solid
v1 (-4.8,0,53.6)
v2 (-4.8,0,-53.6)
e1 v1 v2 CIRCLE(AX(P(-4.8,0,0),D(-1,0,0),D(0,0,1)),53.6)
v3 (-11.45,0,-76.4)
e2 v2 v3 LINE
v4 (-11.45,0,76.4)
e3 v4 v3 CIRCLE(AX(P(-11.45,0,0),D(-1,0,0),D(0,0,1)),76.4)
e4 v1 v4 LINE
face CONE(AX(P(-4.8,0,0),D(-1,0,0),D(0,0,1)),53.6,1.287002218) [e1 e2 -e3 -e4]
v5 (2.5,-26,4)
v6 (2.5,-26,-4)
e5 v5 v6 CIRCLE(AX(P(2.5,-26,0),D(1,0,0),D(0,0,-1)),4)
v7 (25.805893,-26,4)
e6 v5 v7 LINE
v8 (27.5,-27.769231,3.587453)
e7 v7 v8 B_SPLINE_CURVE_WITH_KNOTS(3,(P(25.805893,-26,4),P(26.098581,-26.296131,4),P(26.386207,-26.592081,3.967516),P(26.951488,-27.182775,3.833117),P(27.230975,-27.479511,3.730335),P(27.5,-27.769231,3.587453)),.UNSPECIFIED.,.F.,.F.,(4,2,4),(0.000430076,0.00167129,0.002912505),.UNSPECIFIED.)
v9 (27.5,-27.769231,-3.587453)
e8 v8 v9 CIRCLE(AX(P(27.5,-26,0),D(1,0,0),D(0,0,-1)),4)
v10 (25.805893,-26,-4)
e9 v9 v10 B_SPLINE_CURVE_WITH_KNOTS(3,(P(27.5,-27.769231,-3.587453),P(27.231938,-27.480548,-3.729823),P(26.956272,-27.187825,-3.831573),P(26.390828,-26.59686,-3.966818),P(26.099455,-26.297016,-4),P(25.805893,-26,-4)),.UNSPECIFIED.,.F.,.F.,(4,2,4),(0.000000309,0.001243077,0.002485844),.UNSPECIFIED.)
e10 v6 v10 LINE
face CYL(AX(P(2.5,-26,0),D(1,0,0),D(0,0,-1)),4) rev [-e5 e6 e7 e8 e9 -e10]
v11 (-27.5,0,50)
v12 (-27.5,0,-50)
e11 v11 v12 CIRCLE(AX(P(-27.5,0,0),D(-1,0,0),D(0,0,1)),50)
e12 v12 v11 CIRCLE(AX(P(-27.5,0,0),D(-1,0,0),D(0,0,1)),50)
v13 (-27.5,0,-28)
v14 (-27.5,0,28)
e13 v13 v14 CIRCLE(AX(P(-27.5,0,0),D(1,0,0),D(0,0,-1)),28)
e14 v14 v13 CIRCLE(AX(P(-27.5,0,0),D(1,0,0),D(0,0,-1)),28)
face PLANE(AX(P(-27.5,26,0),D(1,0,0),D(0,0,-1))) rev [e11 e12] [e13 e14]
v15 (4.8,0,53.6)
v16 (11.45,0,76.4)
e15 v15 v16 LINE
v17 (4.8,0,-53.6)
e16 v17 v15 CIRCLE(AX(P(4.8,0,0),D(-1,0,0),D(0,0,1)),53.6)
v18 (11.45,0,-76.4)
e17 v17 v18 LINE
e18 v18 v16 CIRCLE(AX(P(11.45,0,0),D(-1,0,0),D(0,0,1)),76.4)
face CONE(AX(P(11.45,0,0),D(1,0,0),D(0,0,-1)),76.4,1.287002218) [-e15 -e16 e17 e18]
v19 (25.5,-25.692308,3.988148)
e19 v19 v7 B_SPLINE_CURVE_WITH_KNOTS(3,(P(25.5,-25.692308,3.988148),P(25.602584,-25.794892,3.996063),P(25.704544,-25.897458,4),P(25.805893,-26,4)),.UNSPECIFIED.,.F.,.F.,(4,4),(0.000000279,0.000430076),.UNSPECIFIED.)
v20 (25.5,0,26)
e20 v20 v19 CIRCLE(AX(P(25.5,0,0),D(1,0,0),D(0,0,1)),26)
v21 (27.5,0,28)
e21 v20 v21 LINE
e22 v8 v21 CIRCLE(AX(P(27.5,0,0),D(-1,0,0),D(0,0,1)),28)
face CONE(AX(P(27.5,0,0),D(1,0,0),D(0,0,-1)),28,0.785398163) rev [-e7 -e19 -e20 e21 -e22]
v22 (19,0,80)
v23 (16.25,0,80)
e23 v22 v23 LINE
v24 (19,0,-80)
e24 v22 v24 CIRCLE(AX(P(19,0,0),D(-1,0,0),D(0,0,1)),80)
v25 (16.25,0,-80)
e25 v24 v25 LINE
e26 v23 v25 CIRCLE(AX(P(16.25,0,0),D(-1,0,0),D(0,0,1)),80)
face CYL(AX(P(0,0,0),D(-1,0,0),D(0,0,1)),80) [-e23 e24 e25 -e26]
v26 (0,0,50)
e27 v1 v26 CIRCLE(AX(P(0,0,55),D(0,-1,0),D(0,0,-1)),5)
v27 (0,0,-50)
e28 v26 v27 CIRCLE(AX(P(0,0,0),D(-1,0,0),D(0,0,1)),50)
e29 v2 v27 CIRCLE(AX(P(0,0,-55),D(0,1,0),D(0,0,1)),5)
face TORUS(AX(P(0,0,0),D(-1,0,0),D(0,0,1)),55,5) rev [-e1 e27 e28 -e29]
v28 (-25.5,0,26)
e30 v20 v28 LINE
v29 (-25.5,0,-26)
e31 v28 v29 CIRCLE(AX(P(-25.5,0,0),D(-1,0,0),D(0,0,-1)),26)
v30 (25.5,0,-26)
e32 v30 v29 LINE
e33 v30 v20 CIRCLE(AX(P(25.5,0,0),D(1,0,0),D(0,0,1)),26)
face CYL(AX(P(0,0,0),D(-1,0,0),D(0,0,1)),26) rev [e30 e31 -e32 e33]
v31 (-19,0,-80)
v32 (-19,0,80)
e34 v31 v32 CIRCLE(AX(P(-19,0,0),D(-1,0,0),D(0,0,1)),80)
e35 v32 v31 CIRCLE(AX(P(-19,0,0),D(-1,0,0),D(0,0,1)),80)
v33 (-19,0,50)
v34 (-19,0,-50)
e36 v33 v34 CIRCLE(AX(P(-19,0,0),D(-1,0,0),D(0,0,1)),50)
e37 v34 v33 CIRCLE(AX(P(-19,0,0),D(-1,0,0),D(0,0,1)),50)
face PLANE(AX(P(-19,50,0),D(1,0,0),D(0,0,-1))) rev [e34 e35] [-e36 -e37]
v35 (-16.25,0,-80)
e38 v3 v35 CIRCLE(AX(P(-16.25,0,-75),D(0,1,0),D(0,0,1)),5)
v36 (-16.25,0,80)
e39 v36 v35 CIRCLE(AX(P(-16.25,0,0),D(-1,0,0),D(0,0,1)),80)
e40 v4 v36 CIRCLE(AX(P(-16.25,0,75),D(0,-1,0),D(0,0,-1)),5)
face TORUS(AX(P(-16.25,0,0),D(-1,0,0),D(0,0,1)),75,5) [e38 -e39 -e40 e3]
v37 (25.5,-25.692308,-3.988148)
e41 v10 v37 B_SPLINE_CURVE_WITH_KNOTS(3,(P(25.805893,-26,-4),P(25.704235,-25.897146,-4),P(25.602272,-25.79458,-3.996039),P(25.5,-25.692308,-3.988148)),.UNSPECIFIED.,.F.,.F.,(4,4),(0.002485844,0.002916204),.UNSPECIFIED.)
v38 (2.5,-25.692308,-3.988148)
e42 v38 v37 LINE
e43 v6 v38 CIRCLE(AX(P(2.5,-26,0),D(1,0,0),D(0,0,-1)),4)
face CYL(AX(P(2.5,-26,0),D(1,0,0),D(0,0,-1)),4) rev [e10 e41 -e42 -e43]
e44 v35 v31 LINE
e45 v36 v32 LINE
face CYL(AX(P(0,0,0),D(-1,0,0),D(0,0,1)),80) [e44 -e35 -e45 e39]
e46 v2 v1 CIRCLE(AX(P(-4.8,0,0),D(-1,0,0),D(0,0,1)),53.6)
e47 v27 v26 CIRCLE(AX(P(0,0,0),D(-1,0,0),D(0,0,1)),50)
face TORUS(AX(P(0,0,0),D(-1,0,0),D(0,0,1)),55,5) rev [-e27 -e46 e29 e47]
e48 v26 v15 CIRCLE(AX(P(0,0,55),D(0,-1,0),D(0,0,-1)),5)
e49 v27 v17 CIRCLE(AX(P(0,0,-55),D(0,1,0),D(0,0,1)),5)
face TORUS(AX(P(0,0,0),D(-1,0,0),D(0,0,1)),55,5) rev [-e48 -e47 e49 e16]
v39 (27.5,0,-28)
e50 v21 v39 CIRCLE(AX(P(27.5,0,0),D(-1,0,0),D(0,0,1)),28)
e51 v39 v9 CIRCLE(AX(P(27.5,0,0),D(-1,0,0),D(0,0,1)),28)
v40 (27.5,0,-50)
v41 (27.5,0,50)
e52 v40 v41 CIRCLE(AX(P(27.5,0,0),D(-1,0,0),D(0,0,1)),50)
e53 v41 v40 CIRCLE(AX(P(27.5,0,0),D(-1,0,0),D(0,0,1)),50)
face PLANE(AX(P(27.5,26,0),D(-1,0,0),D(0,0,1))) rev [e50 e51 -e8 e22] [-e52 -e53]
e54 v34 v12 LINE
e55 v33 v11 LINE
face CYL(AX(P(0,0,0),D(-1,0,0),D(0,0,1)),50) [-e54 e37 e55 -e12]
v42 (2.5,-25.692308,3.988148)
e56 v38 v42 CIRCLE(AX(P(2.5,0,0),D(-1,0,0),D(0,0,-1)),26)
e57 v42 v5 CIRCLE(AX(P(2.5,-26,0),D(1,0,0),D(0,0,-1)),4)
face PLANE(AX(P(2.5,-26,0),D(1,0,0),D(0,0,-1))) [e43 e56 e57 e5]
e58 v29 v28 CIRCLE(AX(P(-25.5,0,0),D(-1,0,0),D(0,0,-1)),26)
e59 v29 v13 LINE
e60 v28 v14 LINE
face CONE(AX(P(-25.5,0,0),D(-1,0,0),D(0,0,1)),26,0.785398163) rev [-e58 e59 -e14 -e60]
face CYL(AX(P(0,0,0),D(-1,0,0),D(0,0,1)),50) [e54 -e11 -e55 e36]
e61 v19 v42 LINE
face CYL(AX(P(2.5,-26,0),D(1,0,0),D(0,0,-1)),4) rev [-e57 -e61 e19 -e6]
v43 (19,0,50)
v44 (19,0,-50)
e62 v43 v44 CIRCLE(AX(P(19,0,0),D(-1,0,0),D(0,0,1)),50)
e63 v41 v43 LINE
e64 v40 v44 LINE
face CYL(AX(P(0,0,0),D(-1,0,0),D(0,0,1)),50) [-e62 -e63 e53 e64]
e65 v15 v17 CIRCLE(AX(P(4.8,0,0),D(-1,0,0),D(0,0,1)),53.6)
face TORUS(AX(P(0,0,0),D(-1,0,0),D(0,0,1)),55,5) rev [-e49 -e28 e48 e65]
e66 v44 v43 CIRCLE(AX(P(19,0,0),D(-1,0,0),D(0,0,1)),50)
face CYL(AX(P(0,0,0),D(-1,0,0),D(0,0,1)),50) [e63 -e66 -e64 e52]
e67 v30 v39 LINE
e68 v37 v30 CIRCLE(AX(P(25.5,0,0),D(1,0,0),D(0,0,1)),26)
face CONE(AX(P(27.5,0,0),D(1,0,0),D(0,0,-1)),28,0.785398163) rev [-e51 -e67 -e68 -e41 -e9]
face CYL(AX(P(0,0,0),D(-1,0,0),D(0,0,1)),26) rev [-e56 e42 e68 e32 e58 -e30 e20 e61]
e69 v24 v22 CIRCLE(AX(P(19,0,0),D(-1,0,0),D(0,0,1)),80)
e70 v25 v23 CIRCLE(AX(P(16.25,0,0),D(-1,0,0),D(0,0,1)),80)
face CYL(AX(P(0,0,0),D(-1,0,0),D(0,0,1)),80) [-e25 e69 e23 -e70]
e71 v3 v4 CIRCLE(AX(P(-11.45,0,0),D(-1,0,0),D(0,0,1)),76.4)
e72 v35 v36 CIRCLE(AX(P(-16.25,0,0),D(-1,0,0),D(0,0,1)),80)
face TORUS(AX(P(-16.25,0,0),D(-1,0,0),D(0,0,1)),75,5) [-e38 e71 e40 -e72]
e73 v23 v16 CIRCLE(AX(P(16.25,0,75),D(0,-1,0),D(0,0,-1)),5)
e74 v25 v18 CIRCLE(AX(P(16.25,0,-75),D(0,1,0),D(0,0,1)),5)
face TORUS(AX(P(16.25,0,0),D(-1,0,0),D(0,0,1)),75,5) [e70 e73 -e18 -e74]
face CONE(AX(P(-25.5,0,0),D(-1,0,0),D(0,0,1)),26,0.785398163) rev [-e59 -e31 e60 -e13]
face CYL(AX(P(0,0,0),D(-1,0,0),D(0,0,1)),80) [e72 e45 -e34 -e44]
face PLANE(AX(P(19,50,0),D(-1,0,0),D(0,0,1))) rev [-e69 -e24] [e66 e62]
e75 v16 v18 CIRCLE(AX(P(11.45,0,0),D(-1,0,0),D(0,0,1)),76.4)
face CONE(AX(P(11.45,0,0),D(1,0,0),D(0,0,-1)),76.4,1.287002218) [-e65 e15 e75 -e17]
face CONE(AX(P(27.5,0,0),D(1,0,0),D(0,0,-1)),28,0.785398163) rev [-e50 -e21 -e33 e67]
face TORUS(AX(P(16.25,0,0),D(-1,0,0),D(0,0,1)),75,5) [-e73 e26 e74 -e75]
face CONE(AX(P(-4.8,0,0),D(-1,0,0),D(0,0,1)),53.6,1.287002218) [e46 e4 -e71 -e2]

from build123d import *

# Parameters (mm, degrees)
EDGE_CHAMFER_2MM_SIZE = 2
KEYWAY_SKETCH_R       = 4
KEYWAY_CUT_8MM_DEPTH  = 25


with BuildPart() as part:
    # Pulley Profile Sketch → Pulley Body (revolve)
    with BuildSketch(Plane.XY, mode=Mode.PRIVATE) as pulley_body_sk:
        with BuildLine():
            Line((-27.5, 26), (27.5, 26))
            Line((27.5, 26), (27.5, 50))
            Line((27.5, 50), (19, 50))
            Line((19, 50), (19, 80))
            Line((19, 80), (16.25, 80))
            ThreePointArc((16.25, 80), (13.25, 79), (11.45, 76.4))
            Line((11.45, 76.4), (4.8, 53.6))
            ThreePointArc((4.8, 53.6), (0, 50), (-4.8, 53.6))
            Line((-4.8, 53.6), (-11.45, 76.4))
            ThreePointArc((-11.45, 76.4), (-13.25, 79), (-16.25, 80))
            Line((-16.25, 80), (-19, 80))
            Line((-19, 80), (-19, 50))
            Line((-19, 50), (-27.5, 50))
            Line((-27.5, 50), (-27.5, 26))
        make_face()
    revolve(pulley_body_sk.sketch.rotate(Axis((0, 0, 0), (1, 0, 0)), 90), axis=Axis((0, 0, 0), (1, 0, 0)))

    # Edge Chamfer 2mm
    edge_chamfer_2mm_edges = [part.edges().sort_by_distance(p)[0] for p in [
        (27.5, 0, -26),
        (-27.5, 0, -26),
    ]]
    chamfer(edge_chamfer_2mm_edges, length=EDGE_CHAMFER_2MM_SIZE)

    # Keyway Sketch → Keyway Cut 8mm (cut)
    with BuildSketch(Plane(origin=(27.5, 0, 0), x_dir=(0, 0, -1), z_dir=(1, 0, 0))):
        with Locations((0, -26)):
            Circle(KEYWAY_SKETCH_R)
    extrude(amount=-KEYWAY_CUT_8MM_DEPTH, mode=Mode.SUBTRACT)


solid = part.part
